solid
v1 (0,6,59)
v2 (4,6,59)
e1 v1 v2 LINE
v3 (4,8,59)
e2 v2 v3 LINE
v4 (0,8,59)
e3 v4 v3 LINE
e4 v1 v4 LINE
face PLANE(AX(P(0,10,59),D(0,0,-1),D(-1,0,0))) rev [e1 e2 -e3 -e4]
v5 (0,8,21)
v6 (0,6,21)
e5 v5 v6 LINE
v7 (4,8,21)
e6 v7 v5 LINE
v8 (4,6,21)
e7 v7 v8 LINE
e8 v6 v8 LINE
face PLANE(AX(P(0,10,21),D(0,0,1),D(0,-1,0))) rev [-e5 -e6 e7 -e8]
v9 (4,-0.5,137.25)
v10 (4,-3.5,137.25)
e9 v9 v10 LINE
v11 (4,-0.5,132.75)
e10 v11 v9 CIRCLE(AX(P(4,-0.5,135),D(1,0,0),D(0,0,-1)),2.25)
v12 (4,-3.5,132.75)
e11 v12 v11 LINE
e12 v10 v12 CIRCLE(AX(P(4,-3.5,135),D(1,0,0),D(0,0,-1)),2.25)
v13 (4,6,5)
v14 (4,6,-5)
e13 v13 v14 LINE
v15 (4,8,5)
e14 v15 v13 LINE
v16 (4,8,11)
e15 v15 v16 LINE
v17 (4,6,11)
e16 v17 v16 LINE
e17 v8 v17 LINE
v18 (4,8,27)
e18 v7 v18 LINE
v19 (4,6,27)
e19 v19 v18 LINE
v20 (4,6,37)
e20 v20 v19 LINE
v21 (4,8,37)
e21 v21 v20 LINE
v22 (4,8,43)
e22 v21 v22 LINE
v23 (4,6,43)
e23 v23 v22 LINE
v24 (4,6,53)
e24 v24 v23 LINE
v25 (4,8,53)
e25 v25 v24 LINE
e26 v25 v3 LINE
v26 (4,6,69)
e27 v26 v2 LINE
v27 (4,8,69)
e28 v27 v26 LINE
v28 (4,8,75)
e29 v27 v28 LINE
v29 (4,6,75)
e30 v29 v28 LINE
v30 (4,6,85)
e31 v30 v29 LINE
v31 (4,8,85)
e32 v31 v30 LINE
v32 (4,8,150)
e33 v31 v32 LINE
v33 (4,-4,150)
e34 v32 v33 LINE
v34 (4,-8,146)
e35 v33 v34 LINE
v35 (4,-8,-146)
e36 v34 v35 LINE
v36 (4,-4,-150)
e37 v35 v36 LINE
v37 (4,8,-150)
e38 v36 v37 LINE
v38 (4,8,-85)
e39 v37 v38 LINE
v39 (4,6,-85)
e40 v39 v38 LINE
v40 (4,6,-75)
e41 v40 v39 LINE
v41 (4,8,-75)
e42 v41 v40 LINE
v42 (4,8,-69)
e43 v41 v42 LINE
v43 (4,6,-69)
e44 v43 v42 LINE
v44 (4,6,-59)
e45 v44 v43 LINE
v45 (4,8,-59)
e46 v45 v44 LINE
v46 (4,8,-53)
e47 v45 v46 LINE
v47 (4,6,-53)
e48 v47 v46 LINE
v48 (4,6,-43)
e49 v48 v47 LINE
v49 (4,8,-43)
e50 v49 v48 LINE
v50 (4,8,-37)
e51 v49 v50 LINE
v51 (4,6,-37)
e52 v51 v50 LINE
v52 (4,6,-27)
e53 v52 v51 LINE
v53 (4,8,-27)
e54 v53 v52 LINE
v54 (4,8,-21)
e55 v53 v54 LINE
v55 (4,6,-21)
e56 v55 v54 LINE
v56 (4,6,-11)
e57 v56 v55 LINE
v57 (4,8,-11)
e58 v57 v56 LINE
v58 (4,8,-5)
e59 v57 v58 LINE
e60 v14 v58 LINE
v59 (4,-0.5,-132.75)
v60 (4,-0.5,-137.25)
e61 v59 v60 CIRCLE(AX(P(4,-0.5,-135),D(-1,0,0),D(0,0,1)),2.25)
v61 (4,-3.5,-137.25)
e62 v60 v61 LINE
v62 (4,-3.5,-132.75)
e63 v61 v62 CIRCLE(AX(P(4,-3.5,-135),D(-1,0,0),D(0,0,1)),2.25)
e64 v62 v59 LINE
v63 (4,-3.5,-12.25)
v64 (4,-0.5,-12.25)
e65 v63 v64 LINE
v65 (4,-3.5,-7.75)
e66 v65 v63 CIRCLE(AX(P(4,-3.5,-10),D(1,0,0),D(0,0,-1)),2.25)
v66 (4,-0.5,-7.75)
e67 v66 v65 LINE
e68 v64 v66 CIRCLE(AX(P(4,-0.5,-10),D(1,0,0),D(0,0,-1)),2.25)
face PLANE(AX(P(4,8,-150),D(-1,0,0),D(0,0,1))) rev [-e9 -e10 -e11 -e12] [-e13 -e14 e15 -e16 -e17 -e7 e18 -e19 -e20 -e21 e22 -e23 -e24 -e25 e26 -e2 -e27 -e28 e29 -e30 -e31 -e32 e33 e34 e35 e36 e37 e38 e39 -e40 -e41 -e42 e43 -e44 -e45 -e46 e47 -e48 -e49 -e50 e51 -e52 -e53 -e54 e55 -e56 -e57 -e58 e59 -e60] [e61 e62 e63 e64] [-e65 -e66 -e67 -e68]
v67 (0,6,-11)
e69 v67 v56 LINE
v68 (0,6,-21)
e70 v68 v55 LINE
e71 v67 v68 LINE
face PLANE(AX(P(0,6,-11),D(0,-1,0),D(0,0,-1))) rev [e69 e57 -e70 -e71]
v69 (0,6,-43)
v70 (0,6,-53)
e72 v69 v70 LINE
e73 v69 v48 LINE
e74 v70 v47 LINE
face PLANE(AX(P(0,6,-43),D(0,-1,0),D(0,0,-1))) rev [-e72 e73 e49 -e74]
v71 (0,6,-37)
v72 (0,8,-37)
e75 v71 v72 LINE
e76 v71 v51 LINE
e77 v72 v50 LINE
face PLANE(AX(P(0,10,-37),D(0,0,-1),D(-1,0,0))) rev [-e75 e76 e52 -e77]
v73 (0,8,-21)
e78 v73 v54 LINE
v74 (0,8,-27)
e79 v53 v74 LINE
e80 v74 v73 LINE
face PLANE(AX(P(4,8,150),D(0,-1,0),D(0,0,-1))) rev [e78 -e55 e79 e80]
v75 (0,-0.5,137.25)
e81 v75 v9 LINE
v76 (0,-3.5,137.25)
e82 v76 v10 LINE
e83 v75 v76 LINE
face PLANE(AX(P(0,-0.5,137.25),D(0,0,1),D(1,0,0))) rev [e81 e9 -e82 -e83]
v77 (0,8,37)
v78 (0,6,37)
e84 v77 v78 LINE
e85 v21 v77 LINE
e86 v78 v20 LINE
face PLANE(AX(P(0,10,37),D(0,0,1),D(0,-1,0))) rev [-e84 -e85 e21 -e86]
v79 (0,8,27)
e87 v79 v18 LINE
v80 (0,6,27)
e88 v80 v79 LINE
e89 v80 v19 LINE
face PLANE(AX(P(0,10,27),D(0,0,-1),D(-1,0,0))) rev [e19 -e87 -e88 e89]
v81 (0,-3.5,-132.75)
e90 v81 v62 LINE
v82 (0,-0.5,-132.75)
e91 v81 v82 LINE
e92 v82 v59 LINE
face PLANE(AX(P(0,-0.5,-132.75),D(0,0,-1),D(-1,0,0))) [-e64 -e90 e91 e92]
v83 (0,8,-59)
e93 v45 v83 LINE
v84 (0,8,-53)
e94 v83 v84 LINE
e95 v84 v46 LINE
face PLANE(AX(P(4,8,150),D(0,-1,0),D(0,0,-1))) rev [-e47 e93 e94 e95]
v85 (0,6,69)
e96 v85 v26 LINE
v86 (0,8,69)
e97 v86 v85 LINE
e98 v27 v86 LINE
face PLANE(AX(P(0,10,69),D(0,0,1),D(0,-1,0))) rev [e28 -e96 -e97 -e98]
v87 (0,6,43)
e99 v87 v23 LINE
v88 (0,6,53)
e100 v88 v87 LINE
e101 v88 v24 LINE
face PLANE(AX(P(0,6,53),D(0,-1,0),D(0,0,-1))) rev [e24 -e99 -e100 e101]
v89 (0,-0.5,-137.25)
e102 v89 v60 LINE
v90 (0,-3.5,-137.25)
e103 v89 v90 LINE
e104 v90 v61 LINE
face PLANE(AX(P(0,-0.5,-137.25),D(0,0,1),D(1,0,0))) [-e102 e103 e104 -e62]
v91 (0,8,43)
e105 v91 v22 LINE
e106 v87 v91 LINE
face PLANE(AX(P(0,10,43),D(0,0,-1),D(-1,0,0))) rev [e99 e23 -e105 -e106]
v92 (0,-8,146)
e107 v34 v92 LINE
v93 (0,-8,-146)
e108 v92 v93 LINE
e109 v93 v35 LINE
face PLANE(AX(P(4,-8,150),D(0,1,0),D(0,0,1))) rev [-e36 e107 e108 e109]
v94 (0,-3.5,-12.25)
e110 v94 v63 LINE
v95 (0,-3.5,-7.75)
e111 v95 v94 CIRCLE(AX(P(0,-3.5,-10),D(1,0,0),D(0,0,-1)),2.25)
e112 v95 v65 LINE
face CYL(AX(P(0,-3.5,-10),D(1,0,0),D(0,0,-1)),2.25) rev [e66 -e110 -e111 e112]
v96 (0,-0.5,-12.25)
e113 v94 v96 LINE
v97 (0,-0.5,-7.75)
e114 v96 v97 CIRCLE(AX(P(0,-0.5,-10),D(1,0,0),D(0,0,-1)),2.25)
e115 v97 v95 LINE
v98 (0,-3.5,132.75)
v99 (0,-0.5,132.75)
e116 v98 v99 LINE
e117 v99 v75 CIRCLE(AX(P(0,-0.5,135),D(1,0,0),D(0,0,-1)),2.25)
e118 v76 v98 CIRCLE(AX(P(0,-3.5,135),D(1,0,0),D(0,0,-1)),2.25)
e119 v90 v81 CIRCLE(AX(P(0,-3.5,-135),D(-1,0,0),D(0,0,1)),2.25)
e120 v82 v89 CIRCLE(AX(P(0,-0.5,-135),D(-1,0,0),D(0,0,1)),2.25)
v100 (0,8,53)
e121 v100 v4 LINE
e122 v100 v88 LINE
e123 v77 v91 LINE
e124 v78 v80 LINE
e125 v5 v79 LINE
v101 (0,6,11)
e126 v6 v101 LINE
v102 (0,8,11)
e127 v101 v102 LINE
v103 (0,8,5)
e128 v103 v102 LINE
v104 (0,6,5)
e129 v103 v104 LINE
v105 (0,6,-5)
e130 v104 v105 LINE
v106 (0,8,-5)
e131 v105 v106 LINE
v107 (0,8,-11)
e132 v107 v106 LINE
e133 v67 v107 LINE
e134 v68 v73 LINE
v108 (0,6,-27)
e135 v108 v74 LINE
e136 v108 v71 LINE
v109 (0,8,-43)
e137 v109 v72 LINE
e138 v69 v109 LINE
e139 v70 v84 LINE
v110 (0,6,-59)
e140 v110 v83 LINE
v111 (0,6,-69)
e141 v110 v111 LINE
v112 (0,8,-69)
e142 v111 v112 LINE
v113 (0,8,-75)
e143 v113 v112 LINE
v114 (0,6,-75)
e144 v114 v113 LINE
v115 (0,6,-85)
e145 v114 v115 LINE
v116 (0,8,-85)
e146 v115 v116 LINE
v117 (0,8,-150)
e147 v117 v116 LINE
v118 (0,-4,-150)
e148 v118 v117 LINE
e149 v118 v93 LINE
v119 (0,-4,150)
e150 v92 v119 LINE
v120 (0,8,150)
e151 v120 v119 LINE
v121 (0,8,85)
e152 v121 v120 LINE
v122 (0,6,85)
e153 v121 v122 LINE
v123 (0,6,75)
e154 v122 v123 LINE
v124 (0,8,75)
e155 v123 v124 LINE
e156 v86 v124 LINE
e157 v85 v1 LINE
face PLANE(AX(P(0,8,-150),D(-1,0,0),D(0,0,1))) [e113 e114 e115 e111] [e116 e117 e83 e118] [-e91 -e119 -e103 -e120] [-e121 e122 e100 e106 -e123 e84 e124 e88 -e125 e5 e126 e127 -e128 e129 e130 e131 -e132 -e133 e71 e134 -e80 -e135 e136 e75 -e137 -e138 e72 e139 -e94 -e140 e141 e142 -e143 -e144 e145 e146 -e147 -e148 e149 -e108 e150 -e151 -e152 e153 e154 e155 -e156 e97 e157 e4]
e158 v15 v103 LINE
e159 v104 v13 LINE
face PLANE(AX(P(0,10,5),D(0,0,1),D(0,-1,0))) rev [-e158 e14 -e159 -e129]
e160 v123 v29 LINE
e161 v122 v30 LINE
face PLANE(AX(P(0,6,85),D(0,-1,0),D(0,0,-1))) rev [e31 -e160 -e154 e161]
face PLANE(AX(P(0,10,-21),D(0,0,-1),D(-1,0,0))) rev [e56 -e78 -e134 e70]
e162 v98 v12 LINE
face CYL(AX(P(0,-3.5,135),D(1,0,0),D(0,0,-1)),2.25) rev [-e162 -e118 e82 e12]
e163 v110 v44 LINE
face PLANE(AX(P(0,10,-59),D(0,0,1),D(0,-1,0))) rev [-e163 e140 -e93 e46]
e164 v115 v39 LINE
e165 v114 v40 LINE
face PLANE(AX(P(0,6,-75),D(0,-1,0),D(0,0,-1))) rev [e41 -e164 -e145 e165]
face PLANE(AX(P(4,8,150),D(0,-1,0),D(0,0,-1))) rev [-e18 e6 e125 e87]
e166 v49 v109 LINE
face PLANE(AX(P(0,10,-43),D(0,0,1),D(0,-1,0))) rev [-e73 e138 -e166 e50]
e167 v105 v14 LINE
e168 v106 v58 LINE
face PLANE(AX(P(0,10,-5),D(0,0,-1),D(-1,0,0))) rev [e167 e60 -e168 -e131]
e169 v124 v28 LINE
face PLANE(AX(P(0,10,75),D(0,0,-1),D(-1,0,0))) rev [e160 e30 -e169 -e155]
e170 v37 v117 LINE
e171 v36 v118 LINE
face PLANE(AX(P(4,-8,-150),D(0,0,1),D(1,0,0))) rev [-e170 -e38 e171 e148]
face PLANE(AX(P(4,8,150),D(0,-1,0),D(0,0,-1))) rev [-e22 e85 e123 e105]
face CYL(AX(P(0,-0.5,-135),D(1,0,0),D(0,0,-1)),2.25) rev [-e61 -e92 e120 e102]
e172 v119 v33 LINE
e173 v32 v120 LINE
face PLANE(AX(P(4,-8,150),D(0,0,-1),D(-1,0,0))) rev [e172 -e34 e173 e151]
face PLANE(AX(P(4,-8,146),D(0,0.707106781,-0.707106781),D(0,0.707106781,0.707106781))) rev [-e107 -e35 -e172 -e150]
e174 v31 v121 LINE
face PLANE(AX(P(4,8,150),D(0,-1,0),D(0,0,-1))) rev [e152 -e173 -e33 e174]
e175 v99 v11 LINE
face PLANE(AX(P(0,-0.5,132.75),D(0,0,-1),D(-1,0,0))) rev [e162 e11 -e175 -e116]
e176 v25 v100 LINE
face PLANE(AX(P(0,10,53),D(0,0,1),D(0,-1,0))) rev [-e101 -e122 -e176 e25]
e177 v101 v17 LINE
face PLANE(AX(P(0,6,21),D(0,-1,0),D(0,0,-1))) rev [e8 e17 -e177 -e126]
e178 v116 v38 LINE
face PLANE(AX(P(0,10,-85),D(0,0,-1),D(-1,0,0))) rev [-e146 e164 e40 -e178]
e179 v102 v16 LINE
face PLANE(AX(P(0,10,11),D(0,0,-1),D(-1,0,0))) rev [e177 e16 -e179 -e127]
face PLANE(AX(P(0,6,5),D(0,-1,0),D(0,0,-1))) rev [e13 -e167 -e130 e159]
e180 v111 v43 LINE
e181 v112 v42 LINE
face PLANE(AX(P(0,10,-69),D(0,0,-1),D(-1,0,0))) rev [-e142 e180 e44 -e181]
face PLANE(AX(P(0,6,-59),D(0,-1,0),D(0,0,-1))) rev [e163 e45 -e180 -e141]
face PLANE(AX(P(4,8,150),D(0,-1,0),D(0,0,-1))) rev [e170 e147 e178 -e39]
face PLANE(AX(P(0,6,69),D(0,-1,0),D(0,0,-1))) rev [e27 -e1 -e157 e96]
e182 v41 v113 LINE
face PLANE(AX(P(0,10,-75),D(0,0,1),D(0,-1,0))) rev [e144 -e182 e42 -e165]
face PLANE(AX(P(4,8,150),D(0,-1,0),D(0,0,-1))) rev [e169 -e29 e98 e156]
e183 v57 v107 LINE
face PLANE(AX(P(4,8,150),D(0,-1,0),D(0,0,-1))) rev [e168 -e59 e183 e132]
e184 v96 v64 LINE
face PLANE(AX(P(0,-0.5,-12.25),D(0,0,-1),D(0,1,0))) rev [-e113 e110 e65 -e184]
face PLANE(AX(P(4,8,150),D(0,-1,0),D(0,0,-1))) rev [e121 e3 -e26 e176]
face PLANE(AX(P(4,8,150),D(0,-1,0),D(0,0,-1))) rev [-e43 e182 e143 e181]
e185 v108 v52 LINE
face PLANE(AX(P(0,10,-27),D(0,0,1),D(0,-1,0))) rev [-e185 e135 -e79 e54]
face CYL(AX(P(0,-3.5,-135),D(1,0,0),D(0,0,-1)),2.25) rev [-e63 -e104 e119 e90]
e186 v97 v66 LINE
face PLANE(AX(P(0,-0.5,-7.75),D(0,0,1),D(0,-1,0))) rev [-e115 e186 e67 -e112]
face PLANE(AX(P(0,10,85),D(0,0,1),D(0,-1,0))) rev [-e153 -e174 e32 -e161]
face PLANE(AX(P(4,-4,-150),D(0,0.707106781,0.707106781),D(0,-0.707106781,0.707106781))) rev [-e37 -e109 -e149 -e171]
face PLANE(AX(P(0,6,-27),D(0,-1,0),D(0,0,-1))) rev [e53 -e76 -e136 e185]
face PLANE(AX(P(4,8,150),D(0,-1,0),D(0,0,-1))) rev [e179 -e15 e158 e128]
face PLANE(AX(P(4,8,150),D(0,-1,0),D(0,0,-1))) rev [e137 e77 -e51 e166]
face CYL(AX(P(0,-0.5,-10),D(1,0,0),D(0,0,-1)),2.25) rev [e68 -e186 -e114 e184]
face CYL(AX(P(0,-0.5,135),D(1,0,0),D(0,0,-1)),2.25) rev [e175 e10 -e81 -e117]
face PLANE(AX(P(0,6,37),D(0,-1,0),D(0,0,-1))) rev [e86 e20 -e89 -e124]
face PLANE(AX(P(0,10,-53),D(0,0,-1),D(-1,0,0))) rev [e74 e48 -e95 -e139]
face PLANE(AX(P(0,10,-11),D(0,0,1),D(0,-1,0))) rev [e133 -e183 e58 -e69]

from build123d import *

# Parameters (mm, degrees)
SKETCH_1_W                 = 300
SKETCH_1_H                 = 16
BOSS_EXTRUDE_1_DEPTH       = 4
CHAMFER_1_SIZE             = 4
CUT_EXTRUDE_1_DEPTH        = 151.26643005
SKETCH_3_W                 = 10
SKETCH_3_H                 = 4
CUT_EXTRUDE_2_DEPTH        = 151.26643005
LINEAR_PATTERN_1_COUNT     = 6
LINEAR_PATTERN_1_PITCH     = 16
LINEAR_PATTERN_1_COL_COUNT = 6
LINEAR_PATTERN_1_COL_PITCH = 16
CUT_EXTRUDE_3_DEPTH        = 151.26643005


with BuildPart() as part:
    # Sketch 1 → Boss-Extrude 1 (new body)
    with BuildSketch(Plane(origin=(0, 0, 0), x_dir=(0, 0, -1), z_dir=(1, 0, 0))):
        Rectangle(SKETCH_1_W, SKETCH_1_H)
    extrude(amount=BOSS_EXTRUDE_1_DEPTH)

    # Chamfer 1
    chamfer_1_edges = [part.edges().sort_by_distance(p)[0] for p in [
        (2, -8, -150),
        (2, -8, 150),
    ]]
    chamfer(chamfer_1_edges, length=CHAMFER_1_SIZE)

    # Sketch 2 → Cut-Extrude 1 (cut, through all)
    with BuildSketch(Plane(origin=(4, 0, 0), x_dir=(0, 0, -1), z_dir=(1, 0, 0))):
        with BuildLine():
            Line((-132.75, -0.5), (-132.75, -3.5))
            ThreePointArc((-132.75, -3.5), (-135, -5.75), (-137.25, -3.5))
            Line((-137.25, -3.5), (-137.25, -0.5))
            ThreePointArc((-137.25, -0.5), (-135, 1.75), (-132.75, -0.5))
        make_face()
    cut_extrude_1 = extrude(amount=-CUT_EXTRUDE_1_DEPTH, mode=Mode.SUBTRACT)

    # Mirror 1: Cut-Extrude 1 across plane
    add(cut_extrude_1.mirror(Plane.XY), mode=Mode.SUBTRACT)

    # Sketch 3 → Cut-Extrude 2 (cut, through all)
    with BuildSketch(Plane(origin=(4, 0, 0), x_dir=(0, 0, -1), z_dir=(1, 0, 0))):
        with Locations((0, 8)):
            Rectangle(SKETCH_3_W, SKETCH_3_H)
    cut_extrude_2 = extrude(amount=-CUT_EXTRUDE_2_DEPTH, mode=Mode.SUBTRACT)

    # Linear Pattern 1: Cut-Extrude 2 ×6
    with Locations(*[(0, 0, -i * LINEAR_PATTERN_1_PITCH) for i in range(1, LINEAR_PATTERN_1_COUNT)]):
        add(cut_extrude_2, mode=Mode.SUBTRACT)

    # Linear Pattern 1 col: Cut-Extrude 2 ×6
    with Locations(*[(0, 0, i * LINEAR_PATTERN_1_COL_PITCH) for i in range(1, LINEAR_PATTERN_1_COL_COUNT)]):
        add(cut_extrude_2, mode=Mode.SUBTRACT)

    # Sketch 4 → Cut-Extrude 3 (cut, through all)
    with BuildSketch(Plane(origin=(4, 0, 0), x_dir=(0, 0, -1), z_dir=(1, 0, 0))):
        with BuildLine():
            Line((12.25, -0.5), (12.25, -3.5))
            ThreePointArc((12.25, -3.5), (10, -5.75), (7.75, -3.5))
            Line((7.75, -3.5), (7.75, -0.5))
            ThreePointArc((7.75, -0.5), (10, 1.75), (12.25, -0.5))
        make_face()
    extrude(amount=-CUT_EXTRUDE_3_DEPTH, mode=Mode.SUBTRACT)


solid = part.part
